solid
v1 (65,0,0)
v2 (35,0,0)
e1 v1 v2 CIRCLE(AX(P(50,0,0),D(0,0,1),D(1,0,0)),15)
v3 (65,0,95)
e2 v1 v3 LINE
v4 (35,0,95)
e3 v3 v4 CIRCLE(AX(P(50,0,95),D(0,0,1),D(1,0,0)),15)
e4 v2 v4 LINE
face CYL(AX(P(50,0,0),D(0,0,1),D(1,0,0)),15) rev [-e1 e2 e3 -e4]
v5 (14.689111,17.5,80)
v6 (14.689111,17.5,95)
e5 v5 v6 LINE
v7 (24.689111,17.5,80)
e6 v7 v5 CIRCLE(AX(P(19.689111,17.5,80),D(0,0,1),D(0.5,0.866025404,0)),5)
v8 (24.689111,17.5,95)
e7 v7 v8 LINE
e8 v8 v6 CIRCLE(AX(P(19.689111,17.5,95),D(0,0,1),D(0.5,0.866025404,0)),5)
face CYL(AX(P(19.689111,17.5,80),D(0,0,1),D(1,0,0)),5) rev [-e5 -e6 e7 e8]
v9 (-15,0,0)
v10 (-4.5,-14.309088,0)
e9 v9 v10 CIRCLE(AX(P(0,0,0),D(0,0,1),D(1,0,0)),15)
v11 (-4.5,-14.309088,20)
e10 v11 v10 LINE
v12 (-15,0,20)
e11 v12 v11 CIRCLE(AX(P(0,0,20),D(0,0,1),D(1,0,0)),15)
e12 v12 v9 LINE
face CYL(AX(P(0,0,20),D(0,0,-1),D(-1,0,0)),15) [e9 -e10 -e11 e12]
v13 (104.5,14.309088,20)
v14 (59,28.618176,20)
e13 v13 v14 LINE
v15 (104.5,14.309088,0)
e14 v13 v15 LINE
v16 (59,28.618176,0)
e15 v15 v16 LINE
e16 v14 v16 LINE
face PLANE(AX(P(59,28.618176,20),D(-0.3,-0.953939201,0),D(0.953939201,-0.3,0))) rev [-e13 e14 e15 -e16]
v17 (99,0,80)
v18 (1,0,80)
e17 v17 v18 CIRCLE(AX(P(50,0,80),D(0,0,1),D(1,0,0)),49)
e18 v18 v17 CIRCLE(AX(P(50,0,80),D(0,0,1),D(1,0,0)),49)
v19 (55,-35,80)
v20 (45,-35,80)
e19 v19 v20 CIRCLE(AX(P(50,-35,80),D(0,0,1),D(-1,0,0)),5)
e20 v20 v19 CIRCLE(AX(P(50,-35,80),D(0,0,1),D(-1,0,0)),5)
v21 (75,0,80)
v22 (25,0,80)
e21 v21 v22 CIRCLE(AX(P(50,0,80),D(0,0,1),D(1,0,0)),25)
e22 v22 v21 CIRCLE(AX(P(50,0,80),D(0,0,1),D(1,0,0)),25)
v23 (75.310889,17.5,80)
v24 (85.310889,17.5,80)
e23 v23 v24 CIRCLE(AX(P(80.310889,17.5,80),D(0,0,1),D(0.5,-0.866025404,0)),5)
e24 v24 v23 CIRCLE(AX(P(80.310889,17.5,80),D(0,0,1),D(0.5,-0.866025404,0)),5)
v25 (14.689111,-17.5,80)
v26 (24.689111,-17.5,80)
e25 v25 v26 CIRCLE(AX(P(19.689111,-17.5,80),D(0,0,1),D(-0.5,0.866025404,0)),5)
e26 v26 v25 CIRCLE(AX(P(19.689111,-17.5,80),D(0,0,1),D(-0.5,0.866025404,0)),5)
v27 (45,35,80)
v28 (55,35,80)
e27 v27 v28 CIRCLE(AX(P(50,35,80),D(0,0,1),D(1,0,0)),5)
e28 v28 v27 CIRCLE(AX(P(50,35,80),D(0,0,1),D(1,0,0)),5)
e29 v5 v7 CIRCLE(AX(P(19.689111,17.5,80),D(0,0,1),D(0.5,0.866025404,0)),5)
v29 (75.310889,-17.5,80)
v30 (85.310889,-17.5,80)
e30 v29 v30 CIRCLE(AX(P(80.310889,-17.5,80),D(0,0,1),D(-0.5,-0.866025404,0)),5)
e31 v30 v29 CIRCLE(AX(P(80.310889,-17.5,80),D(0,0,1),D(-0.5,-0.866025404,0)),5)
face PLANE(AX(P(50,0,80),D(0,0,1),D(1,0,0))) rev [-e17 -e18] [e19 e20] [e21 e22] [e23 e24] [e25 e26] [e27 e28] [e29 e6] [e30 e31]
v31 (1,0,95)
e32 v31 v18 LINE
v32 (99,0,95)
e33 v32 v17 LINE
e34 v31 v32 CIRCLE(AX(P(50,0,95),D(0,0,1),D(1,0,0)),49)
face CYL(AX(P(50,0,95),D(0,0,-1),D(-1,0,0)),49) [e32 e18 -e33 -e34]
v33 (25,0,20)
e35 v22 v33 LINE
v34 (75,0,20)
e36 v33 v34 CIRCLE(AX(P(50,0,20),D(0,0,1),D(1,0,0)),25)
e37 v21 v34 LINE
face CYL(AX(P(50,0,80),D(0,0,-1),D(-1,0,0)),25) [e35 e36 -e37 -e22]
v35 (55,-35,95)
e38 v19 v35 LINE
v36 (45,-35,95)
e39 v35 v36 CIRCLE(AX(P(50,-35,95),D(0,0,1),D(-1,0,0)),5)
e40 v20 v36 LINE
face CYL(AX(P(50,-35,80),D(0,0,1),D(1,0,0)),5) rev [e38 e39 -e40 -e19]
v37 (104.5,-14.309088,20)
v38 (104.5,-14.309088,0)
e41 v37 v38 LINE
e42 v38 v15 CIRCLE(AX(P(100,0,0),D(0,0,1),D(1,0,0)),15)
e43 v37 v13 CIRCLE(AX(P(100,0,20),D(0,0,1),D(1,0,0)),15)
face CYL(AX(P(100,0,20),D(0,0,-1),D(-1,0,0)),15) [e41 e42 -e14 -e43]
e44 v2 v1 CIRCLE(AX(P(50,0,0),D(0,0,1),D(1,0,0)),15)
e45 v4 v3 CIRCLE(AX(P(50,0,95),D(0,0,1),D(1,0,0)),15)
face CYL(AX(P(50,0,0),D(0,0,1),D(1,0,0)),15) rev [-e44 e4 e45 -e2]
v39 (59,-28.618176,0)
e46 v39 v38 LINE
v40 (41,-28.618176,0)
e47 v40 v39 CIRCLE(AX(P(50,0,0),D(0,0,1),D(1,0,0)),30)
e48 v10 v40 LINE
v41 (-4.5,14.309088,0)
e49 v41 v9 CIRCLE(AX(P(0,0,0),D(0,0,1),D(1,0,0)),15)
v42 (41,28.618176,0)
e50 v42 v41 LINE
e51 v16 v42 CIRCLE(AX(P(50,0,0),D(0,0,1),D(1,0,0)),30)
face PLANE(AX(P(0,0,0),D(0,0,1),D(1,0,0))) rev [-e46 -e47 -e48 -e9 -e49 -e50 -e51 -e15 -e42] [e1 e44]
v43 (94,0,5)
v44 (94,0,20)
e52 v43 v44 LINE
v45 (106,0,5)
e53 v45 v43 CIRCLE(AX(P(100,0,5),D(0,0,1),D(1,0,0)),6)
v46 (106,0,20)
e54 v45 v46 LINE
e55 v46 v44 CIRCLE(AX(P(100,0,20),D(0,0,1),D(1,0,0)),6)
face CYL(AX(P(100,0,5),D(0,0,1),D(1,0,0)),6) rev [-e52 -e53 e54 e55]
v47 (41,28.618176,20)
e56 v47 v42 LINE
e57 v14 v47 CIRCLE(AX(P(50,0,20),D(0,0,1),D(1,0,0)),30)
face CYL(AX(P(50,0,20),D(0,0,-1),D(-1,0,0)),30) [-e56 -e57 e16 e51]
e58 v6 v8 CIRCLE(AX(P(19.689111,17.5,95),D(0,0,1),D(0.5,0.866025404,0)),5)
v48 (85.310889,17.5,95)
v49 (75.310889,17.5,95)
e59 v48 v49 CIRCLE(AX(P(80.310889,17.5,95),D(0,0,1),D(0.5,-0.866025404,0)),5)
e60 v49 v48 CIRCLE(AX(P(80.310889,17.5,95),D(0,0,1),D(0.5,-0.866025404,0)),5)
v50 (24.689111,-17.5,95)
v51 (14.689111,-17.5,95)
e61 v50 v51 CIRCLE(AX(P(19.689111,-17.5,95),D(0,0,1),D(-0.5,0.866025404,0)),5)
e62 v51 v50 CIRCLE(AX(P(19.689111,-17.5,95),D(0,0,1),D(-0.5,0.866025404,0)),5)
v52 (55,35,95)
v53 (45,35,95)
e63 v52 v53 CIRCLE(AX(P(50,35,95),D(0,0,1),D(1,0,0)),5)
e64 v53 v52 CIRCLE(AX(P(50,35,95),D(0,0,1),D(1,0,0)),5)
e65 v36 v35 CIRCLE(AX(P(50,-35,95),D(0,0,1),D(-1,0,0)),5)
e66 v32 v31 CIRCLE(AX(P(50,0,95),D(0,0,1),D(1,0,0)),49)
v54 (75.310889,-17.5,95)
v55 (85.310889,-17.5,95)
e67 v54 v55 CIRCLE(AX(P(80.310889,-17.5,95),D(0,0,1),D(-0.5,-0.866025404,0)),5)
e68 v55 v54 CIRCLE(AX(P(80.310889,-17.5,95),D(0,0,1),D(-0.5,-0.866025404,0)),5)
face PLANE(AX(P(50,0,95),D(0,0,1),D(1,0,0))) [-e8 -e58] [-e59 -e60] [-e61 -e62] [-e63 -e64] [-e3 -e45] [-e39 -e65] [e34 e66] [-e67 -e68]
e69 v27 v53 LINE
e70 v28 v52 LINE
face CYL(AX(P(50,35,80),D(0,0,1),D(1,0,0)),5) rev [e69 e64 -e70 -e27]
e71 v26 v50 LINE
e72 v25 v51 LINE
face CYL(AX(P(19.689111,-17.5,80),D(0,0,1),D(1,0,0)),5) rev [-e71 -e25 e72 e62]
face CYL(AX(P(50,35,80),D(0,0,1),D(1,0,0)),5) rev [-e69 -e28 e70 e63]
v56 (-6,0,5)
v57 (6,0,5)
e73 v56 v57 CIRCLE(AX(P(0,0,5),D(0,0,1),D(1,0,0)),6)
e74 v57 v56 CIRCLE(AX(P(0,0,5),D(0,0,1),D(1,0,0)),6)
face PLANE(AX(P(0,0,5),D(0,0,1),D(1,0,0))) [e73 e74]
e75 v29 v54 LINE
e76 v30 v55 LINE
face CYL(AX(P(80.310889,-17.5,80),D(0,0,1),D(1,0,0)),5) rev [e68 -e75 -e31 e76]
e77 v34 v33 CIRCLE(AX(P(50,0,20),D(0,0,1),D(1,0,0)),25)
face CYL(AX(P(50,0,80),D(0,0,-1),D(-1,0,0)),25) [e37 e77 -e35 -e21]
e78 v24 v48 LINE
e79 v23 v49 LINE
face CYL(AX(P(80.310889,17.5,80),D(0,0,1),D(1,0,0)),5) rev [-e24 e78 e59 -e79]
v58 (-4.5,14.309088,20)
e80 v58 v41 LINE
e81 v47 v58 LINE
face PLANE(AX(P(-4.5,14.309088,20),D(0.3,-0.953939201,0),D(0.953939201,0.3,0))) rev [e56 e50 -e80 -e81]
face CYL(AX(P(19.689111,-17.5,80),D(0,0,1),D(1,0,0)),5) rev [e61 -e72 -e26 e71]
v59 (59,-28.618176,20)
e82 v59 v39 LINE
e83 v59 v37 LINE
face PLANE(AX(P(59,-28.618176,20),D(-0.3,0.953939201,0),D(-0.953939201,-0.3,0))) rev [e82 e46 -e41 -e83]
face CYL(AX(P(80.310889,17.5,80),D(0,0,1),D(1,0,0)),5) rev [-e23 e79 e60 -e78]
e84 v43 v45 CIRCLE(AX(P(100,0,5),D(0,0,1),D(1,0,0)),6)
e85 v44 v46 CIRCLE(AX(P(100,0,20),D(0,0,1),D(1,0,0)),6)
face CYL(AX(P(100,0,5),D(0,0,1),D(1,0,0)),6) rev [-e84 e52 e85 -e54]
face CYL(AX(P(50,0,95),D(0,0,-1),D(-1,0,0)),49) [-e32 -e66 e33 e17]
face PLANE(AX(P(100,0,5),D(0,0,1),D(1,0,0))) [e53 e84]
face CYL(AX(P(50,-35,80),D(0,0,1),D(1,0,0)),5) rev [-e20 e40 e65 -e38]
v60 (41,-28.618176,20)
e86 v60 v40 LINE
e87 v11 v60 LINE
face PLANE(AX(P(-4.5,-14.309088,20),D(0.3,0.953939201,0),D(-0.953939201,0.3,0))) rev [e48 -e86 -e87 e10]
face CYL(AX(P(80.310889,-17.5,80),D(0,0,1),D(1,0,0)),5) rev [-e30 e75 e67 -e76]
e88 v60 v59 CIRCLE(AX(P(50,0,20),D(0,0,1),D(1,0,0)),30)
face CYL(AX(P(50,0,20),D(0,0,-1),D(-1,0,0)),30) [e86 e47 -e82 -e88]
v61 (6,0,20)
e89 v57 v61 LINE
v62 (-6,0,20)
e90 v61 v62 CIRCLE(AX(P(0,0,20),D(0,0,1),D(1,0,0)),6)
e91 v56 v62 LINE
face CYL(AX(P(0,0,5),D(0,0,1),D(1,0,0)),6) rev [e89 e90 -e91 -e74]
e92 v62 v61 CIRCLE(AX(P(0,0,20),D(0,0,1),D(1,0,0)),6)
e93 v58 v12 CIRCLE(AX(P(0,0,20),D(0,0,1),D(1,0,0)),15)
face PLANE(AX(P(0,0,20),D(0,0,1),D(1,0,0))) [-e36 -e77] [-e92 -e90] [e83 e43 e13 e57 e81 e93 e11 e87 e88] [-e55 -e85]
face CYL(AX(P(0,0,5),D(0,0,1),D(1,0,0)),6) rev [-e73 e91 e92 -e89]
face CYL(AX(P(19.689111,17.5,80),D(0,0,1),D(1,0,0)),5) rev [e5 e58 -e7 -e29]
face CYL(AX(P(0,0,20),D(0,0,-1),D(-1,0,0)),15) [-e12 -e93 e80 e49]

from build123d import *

# Parameters (mm, degrees)
MOUNTING_PLATE_DEPTH              = 20
HUB_SKETCH_R                      = 25
HUB_50_DEPTH                      = 60
FLANGE_SKETCH_R                   = 49
FLANGE_98_DEPTH                   = 15
FLANGE_BOLT_HOLE_SKETCH_R         = 5
FLANGE_BOLT_HOLE_10_DEPTH         = 15
BORE_SKETCH_R                     = 15
BORE_CUT_DEPTH                    = 158.006369298
FLANGE_BOLT_HOLE_PATTERN_6X_COUNT = 6
PLATE_HOLES_SKETCH_R              = 6
PLATE_HOLES_2X_12_DEPTH           = 15


with BuildPart() as part:
    # Mounting Plate Sketch → Mounting Plate (new body)
    with BuildSketch(Plane.XY):
        with BuildLine():
            Line((-4.5, 14.309088021), (41, 28.618176043))
            ThreePointArc((41, 28.618176043), (50, 30), (59, 28.618176043))
            Line((59, 28.618176043), (104.5, 14.309088021))
            ThreePointArc((104.5, 14.309088021), (115, 0), (104.5, -14.309088021))
            Line((104.5, -14.309088021), (59, -28.618176043))
            ThreePointArc((59, -28.618176043), (50, -30), (41, -28.618176043))
            Line((41, -28.618176043), (-4.5, -14.309088021))
            ThreePointArc((-4.5, -14.309088021), (-15, 0), (-4.5, 14.309088021))
        make_face()
    extrude(amount=MOUNTING_PLATE_DEPTH)

    # Hub Sketch → Hub Ø50 (add)
    with BuildSketch(Plane.XY.offset(20)):
        with Locations((50, 0)):
            Circle(HUB_SKETCH_R)
    extrude(amount=HUB_50_DEPTH)

    # Flange Sketch → Flange Ø98 (add)
    with BuildSketch(Plane.XY.offset(80)):
        with Locations((50, 0)):
            Circle(FLANGE_SKETCH_R)
    extrude(amount=FLANGE_98_DEPTH)

    # Flange Bolt Hole Sketch → Flange Bolt Hole Ø10 (cut)
    with BuildSketch(Plane.XY.offset(95)):
        with Locations((50, 35)):
            Circle(FLANGE_BOLT_HOLE_SKETCH_R)
    flange_bolt_hole_10 = extrude(amount=-FLANGE_BOLT_HOLE_10_DEPTH, mode=Mode.SUBTRACT)

    # Bore Sketch → Bore Cut (cut, through all)
    with BuildSketch(Plane.XY.offset(95)):
        with Locations((50, 0)):
            Circle(BORE_SKETCH_R)
    extrude(amount=-BORE_CUT_DEPTH, mode=Mode.SUBTRACT)

    # Flange Bolt Hole Pattern 6x: Flange Bolt Hole Ø10 ×6 about axis
    flange_bolt_hole_pattern_6x_axis = Axis((50, 0, 0), (0, 0, 1))
    for i in range(1, FLANGE_BOLT_HOLE_PATTERN_6X_COUNT):
        add(flange_bolt_hole_10.rotate(flange_bolt_hole_pattern_6x_axis, i * 360 / FLANGE_BOLT_HOLE_PATTERN_6X_COUNT), mode=Mode.SUBTRACT)

    # Plate Holes Sketch → Plate Holes 2xØ12 (cut)
    with BuildSketch(Plane.XY.offset(20)):
        Circle(PLATE_HOLES_SKETCH_R)
        with Locations((100, 0)):
            Circle(PLATE_HOLES_SKETCH_R)
    extrude(amount=-PLATE_HOLES_2X_12_DEPTH, mode=Mode.SUBTRACT)


solid = part.part
